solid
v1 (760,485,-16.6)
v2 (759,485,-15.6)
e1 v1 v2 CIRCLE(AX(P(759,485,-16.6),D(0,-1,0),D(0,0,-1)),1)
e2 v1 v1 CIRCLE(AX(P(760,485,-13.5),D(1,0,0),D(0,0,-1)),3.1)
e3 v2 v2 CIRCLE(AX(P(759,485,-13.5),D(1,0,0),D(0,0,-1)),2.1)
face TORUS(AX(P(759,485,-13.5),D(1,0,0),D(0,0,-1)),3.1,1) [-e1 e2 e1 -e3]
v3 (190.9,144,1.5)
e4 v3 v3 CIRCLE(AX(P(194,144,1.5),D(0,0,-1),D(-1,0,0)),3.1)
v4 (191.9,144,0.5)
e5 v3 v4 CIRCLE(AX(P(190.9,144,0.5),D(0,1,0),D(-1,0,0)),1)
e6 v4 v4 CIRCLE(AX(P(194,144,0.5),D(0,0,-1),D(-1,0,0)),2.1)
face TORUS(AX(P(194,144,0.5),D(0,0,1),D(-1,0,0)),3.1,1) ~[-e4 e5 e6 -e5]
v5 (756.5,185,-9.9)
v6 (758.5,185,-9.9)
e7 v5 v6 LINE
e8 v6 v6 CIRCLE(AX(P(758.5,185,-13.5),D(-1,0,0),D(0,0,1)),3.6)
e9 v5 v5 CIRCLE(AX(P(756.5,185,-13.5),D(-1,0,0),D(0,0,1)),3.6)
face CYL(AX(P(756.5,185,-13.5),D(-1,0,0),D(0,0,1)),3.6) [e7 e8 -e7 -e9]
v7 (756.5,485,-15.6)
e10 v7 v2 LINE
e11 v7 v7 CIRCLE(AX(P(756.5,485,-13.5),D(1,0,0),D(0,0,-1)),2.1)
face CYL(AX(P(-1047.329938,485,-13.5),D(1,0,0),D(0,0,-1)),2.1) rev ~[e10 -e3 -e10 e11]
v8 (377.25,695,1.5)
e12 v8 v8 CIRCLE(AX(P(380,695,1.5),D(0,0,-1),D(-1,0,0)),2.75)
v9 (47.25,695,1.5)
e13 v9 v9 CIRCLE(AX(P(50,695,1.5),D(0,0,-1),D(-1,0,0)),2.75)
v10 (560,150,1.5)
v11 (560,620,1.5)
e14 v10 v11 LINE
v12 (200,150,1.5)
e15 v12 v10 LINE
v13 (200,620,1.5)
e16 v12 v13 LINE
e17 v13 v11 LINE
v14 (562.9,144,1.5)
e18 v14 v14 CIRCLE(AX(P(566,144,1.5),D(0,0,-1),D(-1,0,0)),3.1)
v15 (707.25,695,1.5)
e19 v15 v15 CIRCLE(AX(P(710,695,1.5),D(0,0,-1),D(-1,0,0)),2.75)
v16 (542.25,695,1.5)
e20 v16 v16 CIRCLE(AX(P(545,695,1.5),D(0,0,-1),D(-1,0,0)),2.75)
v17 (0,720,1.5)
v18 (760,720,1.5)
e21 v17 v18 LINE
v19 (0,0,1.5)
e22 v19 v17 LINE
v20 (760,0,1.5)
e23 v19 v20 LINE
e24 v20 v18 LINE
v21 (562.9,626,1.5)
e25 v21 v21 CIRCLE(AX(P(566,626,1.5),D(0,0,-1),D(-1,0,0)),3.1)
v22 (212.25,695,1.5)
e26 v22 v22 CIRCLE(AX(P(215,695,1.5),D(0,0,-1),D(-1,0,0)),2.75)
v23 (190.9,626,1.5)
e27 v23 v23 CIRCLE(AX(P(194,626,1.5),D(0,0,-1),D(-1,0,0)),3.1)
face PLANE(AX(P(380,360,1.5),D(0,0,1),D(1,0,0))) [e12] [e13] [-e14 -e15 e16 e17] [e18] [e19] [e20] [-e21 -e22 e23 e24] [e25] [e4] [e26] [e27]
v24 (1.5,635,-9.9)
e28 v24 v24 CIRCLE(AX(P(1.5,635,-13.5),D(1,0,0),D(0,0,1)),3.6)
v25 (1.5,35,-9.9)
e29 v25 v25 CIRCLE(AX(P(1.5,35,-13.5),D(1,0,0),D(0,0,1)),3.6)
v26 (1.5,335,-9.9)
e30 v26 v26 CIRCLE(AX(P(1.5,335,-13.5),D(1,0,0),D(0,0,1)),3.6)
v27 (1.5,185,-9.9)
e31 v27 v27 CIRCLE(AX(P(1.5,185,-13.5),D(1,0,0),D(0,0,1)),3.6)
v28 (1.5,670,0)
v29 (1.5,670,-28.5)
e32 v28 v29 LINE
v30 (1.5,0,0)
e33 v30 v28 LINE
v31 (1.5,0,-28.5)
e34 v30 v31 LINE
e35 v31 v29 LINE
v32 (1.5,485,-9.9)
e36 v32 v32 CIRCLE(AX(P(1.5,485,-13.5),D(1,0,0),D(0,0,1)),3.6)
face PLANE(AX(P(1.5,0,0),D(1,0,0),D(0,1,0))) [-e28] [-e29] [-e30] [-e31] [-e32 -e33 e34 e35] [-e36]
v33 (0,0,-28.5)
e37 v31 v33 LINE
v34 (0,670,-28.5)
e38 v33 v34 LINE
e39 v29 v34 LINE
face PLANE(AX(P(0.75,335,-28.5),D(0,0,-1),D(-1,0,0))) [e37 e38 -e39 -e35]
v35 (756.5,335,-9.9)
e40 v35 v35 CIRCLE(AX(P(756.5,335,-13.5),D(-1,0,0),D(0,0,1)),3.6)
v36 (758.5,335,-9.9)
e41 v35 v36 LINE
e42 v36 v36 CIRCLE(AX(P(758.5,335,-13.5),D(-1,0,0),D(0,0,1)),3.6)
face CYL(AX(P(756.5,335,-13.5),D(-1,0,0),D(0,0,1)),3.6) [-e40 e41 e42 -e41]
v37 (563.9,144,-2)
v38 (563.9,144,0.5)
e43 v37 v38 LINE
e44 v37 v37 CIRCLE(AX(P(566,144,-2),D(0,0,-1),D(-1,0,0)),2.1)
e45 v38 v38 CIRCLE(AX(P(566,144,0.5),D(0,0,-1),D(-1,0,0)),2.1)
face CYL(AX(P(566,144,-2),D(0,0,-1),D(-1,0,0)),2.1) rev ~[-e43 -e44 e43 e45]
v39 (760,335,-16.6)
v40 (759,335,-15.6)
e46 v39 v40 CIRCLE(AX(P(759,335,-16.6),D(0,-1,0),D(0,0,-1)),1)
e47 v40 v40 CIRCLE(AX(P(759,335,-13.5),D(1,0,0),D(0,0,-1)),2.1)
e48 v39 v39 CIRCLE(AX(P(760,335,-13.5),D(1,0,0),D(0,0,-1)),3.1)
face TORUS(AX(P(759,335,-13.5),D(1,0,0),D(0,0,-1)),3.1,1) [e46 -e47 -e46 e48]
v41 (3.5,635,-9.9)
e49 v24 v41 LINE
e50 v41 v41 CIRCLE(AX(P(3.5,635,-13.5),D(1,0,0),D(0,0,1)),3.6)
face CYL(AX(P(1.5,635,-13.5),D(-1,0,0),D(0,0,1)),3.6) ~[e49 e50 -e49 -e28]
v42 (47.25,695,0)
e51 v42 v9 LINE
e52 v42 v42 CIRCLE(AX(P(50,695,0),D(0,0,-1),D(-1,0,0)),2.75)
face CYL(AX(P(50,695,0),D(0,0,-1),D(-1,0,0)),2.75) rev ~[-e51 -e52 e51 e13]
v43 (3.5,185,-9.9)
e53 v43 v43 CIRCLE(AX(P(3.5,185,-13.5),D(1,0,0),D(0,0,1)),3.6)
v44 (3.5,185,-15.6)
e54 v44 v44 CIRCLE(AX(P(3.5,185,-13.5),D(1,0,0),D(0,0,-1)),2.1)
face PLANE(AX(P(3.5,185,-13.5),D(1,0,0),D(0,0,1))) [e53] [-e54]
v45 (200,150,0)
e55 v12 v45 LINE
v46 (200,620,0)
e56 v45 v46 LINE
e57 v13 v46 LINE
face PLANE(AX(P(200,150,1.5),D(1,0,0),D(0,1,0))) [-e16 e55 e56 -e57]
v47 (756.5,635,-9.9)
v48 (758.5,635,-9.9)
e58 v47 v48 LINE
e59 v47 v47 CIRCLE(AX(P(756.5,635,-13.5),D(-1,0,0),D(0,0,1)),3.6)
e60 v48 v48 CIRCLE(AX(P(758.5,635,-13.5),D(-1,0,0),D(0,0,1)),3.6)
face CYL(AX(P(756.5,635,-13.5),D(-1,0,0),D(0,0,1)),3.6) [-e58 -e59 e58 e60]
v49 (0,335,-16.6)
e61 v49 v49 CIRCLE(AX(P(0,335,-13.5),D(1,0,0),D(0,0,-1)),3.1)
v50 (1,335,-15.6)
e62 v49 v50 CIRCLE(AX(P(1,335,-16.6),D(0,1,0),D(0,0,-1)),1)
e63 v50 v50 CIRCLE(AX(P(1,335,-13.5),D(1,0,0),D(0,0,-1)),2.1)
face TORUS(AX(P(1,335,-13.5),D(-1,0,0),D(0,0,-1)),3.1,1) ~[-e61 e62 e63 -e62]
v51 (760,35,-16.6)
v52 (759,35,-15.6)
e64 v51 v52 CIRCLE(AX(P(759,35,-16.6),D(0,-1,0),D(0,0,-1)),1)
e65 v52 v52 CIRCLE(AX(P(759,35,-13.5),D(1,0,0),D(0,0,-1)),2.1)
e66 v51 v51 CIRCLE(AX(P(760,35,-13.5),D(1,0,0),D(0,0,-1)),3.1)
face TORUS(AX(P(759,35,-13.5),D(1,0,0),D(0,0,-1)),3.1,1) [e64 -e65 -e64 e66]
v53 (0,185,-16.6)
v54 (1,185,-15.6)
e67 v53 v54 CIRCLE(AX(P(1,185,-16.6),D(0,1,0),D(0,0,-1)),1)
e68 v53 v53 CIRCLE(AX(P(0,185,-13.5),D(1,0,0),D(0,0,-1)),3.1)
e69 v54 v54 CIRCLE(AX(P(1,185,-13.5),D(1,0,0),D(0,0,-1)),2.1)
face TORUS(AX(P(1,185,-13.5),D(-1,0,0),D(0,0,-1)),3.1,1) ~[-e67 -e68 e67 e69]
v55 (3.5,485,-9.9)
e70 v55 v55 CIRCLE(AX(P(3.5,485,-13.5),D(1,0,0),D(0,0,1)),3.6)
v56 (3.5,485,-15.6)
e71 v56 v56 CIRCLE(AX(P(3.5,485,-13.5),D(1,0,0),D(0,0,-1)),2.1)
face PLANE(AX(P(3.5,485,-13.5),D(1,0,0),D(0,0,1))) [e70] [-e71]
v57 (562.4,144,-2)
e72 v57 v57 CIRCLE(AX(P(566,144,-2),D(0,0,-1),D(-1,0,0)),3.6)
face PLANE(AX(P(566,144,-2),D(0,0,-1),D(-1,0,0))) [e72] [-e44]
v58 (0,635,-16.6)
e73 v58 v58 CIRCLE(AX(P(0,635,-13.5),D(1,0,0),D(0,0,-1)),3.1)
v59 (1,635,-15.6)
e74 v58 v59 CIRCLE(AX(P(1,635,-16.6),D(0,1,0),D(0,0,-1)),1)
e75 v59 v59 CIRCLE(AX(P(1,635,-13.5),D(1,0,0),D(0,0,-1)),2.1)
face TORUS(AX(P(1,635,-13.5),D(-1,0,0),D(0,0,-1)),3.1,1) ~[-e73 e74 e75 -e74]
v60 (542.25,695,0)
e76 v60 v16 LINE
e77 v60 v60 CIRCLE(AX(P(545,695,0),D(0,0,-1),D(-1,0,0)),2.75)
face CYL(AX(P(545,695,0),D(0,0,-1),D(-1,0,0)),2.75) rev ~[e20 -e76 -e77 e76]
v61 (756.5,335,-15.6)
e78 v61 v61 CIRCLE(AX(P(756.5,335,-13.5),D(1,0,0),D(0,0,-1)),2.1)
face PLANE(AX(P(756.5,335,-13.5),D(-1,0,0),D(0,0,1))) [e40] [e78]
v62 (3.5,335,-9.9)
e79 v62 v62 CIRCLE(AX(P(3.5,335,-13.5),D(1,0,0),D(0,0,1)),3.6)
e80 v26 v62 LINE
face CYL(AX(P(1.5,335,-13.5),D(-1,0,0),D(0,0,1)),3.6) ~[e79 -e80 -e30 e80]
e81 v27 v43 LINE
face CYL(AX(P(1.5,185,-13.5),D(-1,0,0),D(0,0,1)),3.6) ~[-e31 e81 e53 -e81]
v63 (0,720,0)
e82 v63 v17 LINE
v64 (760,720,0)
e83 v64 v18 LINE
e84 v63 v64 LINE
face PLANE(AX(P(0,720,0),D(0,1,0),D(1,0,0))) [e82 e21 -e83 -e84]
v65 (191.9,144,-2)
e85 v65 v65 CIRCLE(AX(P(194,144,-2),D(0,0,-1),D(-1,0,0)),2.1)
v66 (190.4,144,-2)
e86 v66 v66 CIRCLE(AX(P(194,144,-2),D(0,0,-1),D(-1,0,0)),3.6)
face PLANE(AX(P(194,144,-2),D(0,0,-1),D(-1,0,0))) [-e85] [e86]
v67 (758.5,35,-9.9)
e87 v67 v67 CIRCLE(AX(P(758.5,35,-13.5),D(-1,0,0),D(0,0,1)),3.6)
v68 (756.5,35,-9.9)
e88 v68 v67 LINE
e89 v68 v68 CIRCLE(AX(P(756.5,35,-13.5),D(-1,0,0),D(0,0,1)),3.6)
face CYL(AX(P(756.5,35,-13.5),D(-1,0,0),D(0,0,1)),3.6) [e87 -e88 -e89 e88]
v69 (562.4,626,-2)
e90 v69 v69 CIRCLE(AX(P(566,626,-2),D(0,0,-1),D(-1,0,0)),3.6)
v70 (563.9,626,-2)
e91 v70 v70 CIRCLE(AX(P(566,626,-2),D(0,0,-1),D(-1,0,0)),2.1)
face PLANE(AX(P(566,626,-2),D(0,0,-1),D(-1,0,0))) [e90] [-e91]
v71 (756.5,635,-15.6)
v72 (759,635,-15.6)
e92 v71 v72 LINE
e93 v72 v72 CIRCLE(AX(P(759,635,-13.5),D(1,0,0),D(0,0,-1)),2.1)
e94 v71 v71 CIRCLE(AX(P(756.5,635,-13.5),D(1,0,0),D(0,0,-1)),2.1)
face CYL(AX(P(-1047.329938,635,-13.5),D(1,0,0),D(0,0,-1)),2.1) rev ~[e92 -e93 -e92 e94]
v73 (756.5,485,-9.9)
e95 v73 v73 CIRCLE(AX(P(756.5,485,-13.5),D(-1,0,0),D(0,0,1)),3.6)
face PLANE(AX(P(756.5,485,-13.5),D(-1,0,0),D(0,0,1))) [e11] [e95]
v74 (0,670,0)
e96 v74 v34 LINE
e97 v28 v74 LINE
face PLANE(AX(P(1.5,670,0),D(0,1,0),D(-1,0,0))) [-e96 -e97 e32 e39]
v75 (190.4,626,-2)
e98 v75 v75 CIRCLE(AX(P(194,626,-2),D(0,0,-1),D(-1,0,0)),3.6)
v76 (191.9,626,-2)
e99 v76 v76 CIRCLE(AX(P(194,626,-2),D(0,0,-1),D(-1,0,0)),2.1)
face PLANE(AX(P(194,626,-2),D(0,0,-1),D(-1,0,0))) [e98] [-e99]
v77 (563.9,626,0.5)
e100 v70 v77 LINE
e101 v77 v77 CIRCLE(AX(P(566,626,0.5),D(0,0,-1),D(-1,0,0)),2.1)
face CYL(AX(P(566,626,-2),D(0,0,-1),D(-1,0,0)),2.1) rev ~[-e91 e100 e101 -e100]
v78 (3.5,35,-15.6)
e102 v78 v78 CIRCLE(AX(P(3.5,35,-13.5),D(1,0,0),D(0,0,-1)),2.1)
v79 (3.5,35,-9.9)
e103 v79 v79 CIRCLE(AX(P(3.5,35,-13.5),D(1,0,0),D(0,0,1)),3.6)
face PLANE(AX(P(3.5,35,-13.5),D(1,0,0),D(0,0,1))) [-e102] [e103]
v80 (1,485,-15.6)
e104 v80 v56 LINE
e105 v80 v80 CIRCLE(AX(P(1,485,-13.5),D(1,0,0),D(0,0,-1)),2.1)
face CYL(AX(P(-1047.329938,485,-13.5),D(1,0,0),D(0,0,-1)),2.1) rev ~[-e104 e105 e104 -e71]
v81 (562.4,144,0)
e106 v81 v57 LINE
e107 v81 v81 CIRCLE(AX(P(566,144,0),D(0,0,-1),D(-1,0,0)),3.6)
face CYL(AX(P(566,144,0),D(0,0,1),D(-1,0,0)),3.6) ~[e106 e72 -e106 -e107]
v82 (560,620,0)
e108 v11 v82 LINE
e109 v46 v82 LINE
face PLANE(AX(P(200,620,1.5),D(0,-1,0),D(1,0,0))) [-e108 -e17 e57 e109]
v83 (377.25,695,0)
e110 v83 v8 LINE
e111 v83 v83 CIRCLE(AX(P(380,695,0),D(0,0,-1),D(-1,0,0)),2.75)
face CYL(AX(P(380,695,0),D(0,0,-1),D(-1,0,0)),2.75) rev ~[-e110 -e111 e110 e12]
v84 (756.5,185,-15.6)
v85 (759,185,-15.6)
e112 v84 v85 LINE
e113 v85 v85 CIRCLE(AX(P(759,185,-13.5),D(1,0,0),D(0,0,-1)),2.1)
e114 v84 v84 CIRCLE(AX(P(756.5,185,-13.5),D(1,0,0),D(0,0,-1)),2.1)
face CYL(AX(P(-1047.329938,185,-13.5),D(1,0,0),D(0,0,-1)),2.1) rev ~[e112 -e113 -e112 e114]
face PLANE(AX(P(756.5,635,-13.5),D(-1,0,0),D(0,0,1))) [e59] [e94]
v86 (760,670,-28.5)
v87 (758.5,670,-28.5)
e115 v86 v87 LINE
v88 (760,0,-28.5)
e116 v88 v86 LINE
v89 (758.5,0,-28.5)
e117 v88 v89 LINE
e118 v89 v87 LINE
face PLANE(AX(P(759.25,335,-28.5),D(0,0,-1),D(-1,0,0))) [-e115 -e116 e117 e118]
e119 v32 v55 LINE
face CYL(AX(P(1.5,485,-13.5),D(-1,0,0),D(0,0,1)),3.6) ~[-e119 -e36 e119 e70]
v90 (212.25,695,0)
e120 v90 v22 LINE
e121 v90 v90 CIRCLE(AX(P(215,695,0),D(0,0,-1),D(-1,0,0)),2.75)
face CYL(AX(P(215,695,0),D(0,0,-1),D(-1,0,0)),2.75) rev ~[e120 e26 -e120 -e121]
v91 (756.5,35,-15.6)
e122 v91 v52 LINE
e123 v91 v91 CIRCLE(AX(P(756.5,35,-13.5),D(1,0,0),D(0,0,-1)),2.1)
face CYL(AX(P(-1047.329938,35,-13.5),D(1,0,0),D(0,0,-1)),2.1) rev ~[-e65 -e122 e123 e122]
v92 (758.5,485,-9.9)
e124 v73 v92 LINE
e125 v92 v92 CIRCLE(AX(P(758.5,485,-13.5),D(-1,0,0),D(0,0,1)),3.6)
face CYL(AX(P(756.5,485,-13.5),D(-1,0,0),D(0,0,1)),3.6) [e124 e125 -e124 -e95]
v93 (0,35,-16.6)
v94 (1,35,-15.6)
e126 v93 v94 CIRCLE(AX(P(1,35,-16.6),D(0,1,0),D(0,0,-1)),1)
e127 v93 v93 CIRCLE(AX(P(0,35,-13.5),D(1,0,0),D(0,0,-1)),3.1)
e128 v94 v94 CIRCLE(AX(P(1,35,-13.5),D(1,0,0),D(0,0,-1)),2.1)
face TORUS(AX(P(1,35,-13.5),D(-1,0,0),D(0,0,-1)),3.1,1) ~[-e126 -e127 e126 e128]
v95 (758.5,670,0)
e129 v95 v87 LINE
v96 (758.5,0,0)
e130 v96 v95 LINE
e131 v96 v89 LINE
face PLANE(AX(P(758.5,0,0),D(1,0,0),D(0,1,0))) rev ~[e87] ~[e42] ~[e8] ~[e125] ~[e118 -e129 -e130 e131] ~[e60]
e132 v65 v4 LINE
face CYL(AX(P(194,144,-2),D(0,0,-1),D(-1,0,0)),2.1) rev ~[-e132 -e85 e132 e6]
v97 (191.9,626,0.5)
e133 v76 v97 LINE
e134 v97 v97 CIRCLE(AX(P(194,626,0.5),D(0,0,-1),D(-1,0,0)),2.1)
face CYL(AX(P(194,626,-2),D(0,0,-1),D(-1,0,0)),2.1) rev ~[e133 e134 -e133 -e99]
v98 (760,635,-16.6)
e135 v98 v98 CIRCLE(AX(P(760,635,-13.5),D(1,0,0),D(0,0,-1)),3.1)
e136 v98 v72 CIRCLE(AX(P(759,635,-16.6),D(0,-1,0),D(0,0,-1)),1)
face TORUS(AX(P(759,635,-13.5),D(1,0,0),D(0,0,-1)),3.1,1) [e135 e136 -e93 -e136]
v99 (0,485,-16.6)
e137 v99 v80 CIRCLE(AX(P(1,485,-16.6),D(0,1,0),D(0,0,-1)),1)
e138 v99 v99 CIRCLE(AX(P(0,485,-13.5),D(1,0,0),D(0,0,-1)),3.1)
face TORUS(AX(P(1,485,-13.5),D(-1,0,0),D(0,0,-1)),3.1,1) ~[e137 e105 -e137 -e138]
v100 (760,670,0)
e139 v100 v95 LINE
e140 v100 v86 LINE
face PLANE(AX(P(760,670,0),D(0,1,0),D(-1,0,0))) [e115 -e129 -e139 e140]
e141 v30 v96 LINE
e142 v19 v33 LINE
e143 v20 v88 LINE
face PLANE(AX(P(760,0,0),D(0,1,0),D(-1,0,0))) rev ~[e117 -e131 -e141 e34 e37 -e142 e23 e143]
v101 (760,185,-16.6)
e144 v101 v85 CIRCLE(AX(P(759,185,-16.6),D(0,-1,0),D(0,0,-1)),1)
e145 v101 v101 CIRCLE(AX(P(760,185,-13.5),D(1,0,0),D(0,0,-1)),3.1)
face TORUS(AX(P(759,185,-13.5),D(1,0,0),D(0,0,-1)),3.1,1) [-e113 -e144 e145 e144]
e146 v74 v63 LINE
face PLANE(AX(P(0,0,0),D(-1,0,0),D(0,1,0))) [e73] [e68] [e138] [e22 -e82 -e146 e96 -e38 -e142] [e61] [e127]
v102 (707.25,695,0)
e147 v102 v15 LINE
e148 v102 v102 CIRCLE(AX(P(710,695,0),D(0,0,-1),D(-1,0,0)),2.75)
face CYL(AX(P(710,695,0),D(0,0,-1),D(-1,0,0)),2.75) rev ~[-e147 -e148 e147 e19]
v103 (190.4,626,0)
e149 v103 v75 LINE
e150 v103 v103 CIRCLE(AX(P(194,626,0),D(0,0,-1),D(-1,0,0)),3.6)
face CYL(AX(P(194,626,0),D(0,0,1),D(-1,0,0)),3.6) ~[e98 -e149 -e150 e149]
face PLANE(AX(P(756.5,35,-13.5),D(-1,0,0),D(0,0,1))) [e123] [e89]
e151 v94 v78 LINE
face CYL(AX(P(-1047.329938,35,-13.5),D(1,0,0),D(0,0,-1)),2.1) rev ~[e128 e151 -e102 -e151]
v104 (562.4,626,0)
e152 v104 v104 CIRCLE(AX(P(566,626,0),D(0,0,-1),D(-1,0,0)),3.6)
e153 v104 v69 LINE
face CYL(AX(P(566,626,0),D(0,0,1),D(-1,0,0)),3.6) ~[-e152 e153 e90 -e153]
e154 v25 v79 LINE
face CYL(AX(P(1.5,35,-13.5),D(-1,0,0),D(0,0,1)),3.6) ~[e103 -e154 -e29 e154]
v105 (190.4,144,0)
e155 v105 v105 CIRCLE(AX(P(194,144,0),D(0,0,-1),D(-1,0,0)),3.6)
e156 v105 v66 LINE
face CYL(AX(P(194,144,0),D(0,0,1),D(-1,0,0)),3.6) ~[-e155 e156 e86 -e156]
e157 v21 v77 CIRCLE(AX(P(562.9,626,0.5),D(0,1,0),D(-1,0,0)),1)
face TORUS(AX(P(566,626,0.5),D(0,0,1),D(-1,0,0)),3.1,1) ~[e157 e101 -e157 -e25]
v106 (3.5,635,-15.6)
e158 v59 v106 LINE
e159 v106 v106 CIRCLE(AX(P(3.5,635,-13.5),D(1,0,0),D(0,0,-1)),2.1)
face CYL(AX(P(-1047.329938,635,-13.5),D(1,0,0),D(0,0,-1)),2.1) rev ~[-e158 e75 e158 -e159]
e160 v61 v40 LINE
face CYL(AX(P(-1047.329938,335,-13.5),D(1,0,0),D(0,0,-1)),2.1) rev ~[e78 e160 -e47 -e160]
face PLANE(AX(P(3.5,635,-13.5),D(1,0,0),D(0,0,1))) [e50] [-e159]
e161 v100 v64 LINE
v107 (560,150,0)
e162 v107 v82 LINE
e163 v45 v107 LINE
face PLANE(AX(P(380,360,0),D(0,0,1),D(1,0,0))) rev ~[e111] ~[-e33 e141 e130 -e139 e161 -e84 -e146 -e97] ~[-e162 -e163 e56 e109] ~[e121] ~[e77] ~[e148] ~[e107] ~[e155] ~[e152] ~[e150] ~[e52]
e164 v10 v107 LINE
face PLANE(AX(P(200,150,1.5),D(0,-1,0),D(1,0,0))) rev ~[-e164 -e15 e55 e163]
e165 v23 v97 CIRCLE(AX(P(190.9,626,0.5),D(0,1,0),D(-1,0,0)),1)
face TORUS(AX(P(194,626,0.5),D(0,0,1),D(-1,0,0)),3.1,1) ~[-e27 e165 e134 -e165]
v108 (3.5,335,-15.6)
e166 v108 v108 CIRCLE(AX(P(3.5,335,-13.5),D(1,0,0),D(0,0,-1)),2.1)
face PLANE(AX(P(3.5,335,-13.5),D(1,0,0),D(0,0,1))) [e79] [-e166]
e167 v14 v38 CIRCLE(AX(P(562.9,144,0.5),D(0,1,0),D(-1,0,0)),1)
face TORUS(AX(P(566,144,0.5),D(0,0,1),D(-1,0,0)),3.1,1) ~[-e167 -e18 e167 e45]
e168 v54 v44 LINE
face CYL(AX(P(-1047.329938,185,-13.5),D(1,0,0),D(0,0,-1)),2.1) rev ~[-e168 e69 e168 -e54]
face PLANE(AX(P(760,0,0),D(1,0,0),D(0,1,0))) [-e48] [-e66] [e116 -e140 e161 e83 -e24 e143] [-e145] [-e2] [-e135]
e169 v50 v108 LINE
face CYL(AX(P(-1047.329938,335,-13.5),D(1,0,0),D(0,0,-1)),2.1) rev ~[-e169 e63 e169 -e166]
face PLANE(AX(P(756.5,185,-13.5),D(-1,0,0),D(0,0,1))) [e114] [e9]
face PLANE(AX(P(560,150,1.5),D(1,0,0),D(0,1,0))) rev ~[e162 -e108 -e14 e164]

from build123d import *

# Parameters (mm, degrees)
SKETCH_1_W          = 760
SKETCH_1_H          = 720
EXTRUDE_1_DEPTH     = 1.5
SKETCH_2_W          = 1.5
SKETCH_2_H          = 670
EXTRUDE_2_DEPTH     = 28.5
SKETCH_3_R          = 2.75
CUT_EXTRUDE_1_DEPTH = 30
SKETCH_5_R          = 3.6
EXTRUDE_3_DEPTH     = 2
EXTRUDE_START       = 2
SKETCH_6_R          = 3.6
EXTRUDE_4_DEPTH     = 2
HOLE_WIZARD_M5_1_D  = 4.2
FILLET_2_R          = 1
SKETCH_9_W          = 360
SKETCH_9_H          = 470
CUT_EXTRUDE_2_DEPTH = 10
SKETCH_10_R         = 3.6
EXTRUDE_5_DEPTH     = 2
SKETCH_11_R         = 2.1
CUT_EXTRUDE_3_DEPTH = 112
FILLET_3_R          = 1


with BuildPart() as part:
    # 草图1 → 凸台-拉伸1 (new body)
    with BuildSketch(Plane.XY):
        with Locations((380, 360)):
            Rectangle(SKETCH_1_W, SKETCH_1_H)
    extrude(amount=EXTRUDE_1_DEPTH)

    # 草图2 → 凸台-拉伸2 (add)
    with BuildSketch(Plane(origin=(0, 0, 0), x_dir=(-1, 0, 0), z_dir=(0, 0, -1))):
        with Locations((-759.25, 335)):
            Rectangle(SKETCH_2_W, SKETCH_2_H)
        with Locations((-0.75, 335)):
            Rectangle(SKETCH_2_W, SKETCH_2_H)
    extrude(amount=EXTRUDE_2_DEPTH)

    # 草图3 → 切除-拉伸1 (cut)
    with BuildSketch(Plane(origin=(0, 0, 0), x_dir=(-1, 0, 0), z_dir=(0, 0, -1))):
        with Locations((-710, 695)):
            Circle(SKETCH_3_R)
        with Locations((-545, 695)):
            Circle(SKETCH_3_R)
        with Locations((-380, 695)):
            Circle(SKETCH_3_R)
        with Locations((-215, 695)):
            Circle(SKETCH_3_R)
        with Locations((-50, 695)):
            Circle(SKETCH_3_R)
    extrude(amount=-CUT_EXTRUDE_1_DEPTH, mode=Mode.SUBTRACT)

    # 草图5 → 凸台-拉伸3 (add)
    with BuildSketch(Plane(origin=(1.5, 0, 0), x_dir=(0, 0, -1), z_dir=(1, 0, 0))):
        with Locations(Location((13.5, 635, 0), (0, 0, 180))):
            Circle(SKETCH_5_R)
        with Locations(Location((13.5, 485, 0), (0, 0, 180))):
            Circle(SKETCH_5_R)
        with Locations(Location((13.5, 335, 0), (0, 0, 180))):
            Circle(SKETCH_5_R)
        with Locations(Location((13.5, 185, 0), (0, 0, 180))):
            Circle(SKETCH_5_R)
        with Locations(Location((13.5, 35, 0), (0, 0, 180))):
            Circle(SKETCH_5_R)
    extrude(amount=EXTRUDE_3_DEPTH)

    # 草图6 → 凸台-拉伸4 (add)
    with BuildSketch(Plane.ZY.offset(-758.5).offset(EXTRUDE_START)):
        with Locations((-13.5, 635)):
            Circle(SKETCH_6_R)
        with Locations((-13.5, 485)):
            Circle(SKETCH_6_R)
        with Locations((-13.5, 335)):
            Circle(SKETCH_6_R)
        with Locations((-13.5, 185)):
            Circle(SKETCH_6_R)
        with Locations((-13.5, 35)):
            Circle(SKETCH_6_R)
    extrude(amount=-EXTRUDE_4_DEPTH)

    # M5 螺纹孔1 (through all)
    with Locations(Plane.ZY):
        with Locations((-13.5, 635), (-13.5, 485), (-13.5, 335), (-13.5, 185), (-13.5, 35)):
            Hole(HOLE_WIZARD_M5_1_D / 2)

    # 圆角2
    fillet_2_edges = [part.edges().sort_by_distance(p)[0] for p in [
        (760, 35, -11.4),
        (0, 35, -11.4),
        (760, 185, -11.4),
        (0, 185, -11.4),
        (760, 335, -11.4),
        (0, 335, -11.4),
        (760, 485, -11.4),
        (0, 485, -11.4),
        (760, 635, -11.4),
        (0, 635, -11.4),
    ]]
    fillet(fillet_2_edges, radius=FILLET_2_R)

    # 草图9 → 切除-拉伸2 (cut)
    with BuildSketch(Plane.XY.offset(1.5)):
        with Locations((380, 385)):
            Rectangle(SKETCH_9_W, SKETCH_9_H)
    extrude(amount=-CUT_EXTRUDE_2_DEPTH, mode=Mode.SUBTRACT)

    # 草图10 → 凸台-拉伸5 (add)
    with BuildSketch(Plane(origin=(0, 0, 0), x_dir=(-1, 0, 0), z_dir=(0, 0, -1))):
        with Locations((-566, 626)):
            Circle(SKETCH_10_R)
        with Locations((-194, 626)):
            Circle(SKETCH_10_R)
        with Locations((-194, 144)):
            Circle(SKETCH_10_R)
        with Locations((-566, 144)):
            Circle(SKETCH_10_R)
    extrude(amount=EXTRUDE_5_DEPTH)

    # 草图11 → 切除-拉伸3 (cut)
    with BuildSketch(Plane(origin=(0, 0, -2), x_dir=(-1, 0, 0), z_dir=(0, 0, -1))):
        with Locations((-566, 626)):
            Circle(SKETCH_11_R)
        with Locations((-194, 626)):
            Circle(SKETCH_11_R)
        with Locations((-194, 144)):
            Circle(SKETCH_11_R)
        with Locations((-566, 144)):
            Circle(SKETCH_11_R)
    extrude(amount=-CUT_EXTRUDE_3_DEPTH, mode=Mode.SUBTRACT)

    # 圆角3
    fillet_3_edges = [part.edges().sort_by_distance(p)[0] for p in [
        (568.1, 626, 1.5),
        (196.1, 626, 1.5),
        (196.1, 144, 1.5),
        (568.1, 144, 1.5),
    ]]
    fillet(fillet_3_edges, radius=FILLET_3_R)


solid = part.part
